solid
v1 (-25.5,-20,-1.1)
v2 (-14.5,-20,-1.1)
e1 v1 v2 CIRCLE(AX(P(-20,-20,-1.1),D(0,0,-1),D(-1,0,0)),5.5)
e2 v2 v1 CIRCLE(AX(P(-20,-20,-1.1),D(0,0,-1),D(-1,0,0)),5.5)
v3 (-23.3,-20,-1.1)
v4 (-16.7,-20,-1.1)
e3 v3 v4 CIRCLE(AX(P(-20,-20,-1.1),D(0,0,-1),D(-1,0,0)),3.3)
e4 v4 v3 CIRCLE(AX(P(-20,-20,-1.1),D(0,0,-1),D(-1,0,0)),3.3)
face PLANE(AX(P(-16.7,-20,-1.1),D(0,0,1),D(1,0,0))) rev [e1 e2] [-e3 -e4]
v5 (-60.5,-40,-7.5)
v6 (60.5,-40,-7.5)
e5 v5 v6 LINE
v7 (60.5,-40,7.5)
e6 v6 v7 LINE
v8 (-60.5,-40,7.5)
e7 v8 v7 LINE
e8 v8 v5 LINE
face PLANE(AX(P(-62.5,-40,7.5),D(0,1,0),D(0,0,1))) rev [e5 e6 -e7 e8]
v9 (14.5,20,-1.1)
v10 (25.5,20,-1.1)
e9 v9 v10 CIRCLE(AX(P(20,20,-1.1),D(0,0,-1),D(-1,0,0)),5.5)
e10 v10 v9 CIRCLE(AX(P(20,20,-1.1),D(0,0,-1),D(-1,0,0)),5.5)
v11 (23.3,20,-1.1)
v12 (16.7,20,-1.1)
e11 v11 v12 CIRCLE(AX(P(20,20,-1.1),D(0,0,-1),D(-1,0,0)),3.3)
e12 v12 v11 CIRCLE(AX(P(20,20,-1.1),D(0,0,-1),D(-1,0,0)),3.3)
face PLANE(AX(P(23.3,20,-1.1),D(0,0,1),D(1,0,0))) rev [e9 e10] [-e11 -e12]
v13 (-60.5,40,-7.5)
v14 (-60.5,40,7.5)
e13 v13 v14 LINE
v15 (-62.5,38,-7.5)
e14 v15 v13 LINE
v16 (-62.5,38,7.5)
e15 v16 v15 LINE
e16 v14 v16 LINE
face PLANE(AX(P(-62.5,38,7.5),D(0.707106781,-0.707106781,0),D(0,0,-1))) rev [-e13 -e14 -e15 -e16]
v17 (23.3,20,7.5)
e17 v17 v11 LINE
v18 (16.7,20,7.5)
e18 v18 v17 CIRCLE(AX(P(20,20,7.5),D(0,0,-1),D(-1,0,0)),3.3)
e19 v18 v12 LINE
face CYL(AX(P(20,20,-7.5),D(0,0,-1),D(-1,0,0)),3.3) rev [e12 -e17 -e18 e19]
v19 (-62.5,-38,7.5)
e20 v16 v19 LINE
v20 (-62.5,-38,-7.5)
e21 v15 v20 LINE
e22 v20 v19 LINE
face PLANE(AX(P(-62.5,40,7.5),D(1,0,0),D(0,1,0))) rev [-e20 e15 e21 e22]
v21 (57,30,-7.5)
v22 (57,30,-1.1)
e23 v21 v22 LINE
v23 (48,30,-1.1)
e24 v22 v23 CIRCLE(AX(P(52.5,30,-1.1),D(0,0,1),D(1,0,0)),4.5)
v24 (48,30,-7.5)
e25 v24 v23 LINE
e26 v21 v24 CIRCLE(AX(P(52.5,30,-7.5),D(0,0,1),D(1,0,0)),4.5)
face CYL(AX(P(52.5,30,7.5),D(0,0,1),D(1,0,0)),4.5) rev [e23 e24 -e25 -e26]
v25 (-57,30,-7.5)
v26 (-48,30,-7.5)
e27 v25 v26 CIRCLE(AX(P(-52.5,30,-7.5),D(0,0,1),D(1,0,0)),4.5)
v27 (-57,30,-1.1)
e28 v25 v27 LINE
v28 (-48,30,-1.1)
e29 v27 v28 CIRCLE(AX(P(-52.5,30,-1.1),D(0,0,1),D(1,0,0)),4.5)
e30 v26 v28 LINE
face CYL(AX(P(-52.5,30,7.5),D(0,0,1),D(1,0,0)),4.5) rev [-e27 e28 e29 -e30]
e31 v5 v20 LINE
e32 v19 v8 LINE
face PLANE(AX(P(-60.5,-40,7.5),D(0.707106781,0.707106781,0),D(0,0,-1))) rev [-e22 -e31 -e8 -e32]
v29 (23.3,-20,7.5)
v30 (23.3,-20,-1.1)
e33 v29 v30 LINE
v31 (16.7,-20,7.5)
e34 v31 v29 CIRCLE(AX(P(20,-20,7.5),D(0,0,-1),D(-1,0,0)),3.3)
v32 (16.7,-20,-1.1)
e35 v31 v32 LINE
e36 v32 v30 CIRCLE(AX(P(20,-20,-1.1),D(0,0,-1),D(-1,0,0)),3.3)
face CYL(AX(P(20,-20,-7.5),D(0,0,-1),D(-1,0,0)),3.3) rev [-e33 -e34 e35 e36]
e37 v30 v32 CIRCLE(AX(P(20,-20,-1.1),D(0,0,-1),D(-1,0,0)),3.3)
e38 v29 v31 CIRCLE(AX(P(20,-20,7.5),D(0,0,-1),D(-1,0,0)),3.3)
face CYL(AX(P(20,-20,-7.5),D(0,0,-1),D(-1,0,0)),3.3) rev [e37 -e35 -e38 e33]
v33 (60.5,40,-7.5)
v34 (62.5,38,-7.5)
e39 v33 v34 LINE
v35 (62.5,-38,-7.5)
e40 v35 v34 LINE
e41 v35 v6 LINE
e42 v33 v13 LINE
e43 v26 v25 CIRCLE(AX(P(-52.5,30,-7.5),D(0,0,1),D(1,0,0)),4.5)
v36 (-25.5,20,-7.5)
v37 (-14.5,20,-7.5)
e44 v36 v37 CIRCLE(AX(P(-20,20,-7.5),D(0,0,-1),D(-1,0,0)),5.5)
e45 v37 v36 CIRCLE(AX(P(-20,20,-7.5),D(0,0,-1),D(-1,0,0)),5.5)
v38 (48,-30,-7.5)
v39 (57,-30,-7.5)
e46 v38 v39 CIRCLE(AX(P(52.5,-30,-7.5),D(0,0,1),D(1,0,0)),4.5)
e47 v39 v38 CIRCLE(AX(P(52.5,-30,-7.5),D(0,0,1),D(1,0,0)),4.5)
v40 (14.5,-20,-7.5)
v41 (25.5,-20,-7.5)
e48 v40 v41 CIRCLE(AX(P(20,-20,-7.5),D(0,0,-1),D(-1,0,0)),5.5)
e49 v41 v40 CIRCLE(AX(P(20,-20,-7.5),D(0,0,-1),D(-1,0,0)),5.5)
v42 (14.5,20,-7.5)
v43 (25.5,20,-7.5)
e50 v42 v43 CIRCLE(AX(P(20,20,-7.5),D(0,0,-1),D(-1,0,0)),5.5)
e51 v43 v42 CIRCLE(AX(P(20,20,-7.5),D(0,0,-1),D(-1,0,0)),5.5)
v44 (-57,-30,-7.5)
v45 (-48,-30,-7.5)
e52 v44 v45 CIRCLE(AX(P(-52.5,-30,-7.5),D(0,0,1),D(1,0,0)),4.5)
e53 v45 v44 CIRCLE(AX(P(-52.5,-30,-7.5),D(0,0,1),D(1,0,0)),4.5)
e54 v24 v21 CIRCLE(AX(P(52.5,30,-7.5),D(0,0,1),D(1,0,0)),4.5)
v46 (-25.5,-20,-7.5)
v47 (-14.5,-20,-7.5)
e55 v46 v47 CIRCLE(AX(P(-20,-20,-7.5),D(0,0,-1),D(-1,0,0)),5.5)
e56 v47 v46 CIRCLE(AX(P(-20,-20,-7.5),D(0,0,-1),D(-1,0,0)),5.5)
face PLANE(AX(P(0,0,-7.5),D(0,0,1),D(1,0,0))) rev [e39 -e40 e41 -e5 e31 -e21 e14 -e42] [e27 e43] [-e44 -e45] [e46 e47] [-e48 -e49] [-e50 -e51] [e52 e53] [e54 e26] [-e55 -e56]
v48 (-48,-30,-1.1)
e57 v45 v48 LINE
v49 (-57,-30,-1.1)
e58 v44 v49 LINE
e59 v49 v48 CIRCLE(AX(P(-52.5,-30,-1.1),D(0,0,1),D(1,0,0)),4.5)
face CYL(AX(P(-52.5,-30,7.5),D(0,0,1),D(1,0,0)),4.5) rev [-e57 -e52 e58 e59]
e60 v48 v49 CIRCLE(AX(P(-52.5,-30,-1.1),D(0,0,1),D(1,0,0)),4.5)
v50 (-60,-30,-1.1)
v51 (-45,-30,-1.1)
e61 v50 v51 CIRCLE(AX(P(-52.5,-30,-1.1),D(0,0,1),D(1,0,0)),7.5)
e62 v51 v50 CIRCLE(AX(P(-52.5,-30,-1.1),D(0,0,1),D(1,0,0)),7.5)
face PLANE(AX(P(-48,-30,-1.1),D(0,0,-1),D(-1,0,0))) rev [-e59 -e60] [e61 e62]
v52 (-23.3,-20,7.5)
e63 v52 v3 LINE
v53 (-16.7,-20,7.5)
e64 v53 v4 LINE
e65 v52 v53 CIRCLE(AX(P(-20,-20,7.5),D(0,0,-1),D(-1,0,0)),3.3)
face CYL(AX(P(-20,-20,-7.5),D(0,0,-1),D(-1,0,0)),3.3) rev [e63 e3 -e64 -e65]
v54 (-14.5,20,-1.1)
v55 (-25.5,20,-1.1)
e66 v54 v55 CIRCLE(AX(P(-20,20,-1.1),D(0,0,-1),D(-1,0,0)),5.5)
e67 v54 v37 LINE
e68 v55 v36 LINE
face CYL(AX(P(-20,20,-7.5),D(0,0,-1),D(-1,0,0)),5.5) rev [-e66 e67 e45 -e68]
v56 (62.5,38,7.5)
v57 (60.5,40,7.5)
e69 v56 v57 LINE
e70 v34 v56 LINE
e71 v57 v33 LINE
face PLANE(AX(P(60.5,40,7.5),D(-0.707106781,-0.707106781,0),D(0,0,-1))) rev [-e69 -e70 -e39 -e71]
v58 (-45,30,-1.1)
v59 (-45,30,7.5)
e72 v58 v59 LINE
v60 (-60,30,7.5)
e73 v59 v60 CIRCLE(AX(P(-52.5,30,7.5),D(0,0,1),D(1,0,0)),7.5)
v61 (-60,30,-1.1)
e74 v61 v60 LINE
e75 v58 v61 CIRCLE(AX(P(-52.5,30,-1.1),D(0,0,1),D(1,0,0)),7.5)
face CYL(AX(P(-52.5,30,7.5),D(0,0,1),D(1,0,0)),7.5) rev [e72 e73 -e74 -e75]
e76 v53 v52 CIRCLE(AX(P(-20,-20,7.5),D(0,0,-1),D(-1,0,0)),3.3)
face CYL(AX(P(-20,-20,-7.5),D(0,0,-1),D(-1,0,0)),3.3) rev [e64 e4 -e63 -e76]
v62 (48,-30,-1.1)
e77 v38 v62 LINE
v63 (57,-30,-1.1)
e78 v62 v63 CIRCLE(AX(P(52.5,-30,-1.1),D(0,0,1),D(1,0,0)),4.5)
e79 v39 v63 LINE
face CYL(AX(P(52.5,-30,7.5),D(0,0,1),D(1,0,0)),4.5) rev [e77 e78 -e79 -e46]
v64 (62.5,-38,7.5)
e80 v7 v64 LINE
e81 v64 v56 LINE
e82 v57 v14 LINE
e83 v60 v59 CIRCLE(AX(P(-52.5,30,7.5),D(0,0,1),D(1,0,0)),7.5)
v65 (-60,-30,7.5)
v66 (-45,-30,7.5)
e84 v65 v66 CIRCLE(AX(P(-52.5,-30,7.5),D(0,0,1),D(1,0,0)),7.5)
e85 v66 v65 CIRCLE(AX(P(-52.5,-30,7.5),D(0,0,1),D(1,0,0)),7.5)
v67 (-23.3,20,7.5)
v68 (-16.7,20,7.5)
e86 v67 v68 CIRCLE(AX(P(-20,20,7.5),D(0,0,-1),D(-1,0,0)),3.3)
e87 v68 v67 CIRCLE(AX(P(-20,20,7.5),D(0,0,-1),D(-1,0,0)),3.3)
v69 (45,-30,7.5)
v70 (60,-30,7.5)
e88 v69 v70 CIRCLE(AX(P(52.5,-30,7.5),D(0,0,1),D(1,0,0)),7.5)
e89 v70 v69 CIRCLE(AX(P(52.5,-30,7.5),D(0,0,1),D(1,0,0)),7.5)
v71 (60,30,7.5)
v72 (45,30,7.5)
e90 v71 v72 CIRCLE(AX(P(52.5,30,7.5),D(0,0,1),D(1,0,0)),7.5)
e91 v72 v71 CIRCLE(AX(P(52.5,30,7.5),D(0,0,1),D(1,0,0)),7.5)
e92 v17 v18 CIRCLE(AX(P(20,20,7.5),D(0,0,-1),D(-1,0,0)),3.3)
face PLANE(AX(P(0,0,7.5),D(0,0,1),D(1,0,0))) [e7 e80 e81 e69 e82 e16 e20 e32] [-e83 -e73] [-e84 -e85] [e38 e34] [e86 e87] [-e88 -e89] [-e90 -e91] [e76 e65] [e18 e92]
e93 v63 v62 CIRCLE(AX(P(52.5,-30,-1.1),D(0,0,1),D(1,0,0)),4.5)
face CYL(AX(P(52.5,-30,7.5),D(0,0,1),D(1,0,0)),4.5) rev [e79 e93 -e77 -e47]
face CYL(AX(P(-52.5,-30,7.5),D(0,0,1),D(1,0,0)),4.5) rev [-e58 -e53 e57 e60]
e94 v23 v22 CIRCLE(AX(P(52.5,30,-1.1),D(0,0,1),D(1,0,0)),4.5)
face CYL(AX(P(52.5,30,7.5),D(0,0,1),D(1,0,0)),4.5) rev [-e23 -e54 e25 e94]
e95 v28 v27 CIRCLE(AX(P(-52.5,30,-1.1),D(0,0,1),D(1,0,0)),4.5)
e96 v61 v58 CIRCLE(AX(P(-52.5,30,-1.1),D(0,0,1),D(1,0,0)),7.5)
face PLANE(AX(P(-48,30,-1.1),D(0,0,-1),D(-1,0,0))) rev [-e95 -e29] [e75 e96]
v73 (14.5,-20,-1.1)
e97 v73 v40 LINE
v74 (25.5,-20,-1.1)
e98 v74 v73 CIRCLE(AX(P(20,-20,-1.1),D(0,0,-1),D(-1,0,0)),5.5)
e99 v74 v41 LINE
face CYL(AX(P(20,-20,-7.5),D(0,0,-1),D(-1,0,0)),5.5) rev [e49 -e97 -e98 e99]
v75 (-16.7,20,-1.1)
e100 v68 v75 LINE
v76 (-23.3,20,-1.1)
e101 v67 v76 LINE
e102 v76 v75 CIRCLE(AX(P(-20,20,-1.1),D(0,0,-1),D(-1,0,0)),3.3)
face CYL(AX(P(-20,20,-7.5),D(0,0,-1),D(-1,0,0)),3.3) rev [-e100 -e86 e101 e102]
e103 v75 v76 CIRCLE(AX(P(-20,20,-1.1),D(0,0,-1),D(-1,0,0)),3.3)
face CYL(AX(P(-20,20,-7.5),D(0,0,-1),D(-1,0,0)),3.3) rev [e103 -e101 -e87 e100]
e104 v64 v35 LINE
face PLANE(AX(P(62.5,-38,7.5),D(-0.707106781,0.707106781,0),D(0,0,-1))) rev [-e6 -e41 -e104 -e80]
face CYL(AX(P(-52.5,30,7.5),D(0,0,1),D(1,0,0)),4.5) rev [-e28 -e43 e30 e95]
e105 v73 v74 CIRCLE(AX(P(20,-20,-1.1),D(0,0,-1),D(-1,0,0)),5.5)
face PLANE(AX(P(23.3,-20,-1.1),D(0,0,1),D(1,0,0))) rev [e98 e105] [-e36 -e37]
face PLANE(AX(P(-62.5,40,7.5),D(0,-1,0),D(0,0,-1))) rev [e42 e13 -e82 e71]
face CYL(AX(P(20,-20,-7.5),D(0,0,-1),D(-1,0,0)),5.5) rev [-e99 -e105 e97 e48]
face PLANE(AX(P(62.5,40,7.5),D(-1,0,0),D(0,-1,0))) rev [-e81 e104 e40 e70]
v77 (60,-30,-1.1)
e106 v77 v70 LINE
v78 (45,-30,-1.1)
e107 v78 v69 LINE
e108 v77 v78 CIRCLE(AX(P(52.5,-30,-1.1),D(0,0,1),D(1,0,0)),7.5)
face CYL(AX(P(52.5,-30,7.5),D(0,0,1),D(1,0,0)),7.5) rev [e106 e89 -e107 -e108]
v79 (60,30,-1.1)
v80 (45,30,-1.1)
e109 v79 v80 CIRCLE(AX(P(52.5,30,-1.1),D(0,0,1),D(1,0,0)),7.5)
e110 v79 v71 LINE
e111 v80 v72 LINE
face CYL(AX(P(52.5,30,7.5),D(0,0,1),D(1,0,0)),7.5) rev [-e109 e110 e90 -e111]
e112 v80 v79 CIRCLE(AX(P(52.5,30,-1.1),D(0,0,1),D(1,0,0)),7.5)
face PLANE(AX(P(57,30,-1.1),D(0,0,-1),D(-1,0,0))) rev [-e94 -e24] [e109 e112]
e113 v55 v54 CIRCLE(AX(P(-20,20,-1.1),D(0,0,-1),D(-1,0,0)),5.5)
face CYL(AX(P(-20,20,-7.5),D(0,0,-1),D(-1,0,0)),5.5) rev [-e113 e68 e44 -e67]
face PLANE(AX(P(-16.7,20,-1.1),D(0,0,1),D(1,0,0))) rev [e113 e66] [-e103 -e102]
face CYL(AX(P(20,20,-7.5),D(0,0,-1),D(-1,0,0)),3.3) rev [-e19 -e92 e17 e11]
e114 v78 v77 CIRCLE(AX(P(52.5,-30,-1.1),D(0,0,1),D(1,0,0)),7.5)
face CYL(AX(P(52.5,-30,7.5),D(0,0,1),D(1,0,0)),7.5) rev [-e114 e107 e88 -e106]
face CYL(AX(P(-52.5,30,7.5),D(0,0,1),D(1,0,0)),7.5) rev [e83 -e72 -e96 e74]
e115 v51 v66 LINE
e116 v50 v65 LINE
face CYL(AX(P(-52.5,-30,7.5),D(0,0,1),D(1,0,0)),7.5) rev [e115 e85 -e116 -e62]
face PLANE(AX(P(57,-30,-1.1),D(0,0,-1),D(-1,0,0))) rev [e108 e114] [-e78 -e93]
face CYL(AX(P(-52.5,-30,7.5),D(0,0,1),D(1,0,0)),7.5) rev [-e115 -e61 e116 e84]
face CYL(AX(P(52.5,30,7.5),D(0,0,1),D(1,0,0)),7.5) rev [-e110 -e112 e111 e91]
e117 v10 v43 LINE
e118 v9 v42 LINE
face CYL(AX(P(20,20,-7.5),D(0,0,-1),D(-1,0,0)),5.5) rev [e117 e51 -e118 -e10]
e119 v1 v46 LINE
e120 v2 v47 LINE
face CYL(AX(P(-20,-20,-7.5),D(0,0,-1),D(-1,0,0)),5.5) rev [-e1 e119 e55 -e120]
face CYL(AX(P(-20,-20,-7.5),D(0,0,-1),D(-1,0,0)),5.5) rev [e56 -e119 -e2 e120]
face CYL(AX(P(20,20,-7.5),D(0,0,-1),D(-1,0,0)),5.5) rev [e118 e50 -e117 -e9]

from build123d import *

# Parameters (mm, degrees)
SKETCH_1_W                   = 125
SKETCH_1_H                   = 80
EXTRUDE_1_DEPTH              = 7.5
HOLE_WIZARD_M8_1_D           = 9
HOLE_WIZARD_M8_1_CBORE_D     = 15
HOLE_WIZARD_M8_1_CBORE_DEPTH = 8.6
HOLE_WIZARD_M6_1_D           = 6.6
HOLE_WIZARD_M6_1_CBORE_D     = 11
HOLE_WIZARD_M6_1_CBORE_DEPTH = 6.4
CHAMFER_1_SIZE               = 2


with BuildPart() as part:
    # 草图1 → 凸台-拉伸1 (new, symmetric)
    with BuildSketch(Plane.XY):
        Rectangle(SKETCH_1_W, SKETCH_1_H)
    extrude(amount=EXTRUDE_1_DEPTH, both=True)

    # M8 六角凹头螺钉的柱形沉头孔1 (through all)
    with Locations(Plane.XY.offset(7.5)):
        with Locations((-52.5, 30), (-52.5, -30), (52.5, -30), (52.5, 30)):
            CounterBoreHole(HOLE_WIZARD_M8_1_D / 2, HOLE_WIZARD_M8_1_CBORE_D / 2, HOLE_WIZARD_M8_1_CBORE_DEPTH)

    # M6 六角凹头螺钉的柱形沉头孔1 (through all)
    with Locations(Plane(origin=(0, 0, -7.5), x_dir=(-1, 0, 0), z_dir=(0, 0, -1))):
        with Locations((-20, -20), (-20, 20), (20, -20), (20, 20)):
            CounterBoreHole(HOLE_WIZARD_M6_1_D / 2, HOLE_WIZARD_M6_1_CBORE_D / 2, HOLE_WIZARD_M6_1_CBORE_DEPTH)

    # 倒角1
    chamfer_1_edges = [part.edges().sort_by_distance(p)[0] for p in [
        (62.5, -40, 0),
        (-62.5, -40, 0),
        (-62.5, 40, 0),
        (62.5, 40, 0),
    ]]
    chamfer(chamfer_1_edges, length=CHAMFER_1_SIZE)


solid = part.part
